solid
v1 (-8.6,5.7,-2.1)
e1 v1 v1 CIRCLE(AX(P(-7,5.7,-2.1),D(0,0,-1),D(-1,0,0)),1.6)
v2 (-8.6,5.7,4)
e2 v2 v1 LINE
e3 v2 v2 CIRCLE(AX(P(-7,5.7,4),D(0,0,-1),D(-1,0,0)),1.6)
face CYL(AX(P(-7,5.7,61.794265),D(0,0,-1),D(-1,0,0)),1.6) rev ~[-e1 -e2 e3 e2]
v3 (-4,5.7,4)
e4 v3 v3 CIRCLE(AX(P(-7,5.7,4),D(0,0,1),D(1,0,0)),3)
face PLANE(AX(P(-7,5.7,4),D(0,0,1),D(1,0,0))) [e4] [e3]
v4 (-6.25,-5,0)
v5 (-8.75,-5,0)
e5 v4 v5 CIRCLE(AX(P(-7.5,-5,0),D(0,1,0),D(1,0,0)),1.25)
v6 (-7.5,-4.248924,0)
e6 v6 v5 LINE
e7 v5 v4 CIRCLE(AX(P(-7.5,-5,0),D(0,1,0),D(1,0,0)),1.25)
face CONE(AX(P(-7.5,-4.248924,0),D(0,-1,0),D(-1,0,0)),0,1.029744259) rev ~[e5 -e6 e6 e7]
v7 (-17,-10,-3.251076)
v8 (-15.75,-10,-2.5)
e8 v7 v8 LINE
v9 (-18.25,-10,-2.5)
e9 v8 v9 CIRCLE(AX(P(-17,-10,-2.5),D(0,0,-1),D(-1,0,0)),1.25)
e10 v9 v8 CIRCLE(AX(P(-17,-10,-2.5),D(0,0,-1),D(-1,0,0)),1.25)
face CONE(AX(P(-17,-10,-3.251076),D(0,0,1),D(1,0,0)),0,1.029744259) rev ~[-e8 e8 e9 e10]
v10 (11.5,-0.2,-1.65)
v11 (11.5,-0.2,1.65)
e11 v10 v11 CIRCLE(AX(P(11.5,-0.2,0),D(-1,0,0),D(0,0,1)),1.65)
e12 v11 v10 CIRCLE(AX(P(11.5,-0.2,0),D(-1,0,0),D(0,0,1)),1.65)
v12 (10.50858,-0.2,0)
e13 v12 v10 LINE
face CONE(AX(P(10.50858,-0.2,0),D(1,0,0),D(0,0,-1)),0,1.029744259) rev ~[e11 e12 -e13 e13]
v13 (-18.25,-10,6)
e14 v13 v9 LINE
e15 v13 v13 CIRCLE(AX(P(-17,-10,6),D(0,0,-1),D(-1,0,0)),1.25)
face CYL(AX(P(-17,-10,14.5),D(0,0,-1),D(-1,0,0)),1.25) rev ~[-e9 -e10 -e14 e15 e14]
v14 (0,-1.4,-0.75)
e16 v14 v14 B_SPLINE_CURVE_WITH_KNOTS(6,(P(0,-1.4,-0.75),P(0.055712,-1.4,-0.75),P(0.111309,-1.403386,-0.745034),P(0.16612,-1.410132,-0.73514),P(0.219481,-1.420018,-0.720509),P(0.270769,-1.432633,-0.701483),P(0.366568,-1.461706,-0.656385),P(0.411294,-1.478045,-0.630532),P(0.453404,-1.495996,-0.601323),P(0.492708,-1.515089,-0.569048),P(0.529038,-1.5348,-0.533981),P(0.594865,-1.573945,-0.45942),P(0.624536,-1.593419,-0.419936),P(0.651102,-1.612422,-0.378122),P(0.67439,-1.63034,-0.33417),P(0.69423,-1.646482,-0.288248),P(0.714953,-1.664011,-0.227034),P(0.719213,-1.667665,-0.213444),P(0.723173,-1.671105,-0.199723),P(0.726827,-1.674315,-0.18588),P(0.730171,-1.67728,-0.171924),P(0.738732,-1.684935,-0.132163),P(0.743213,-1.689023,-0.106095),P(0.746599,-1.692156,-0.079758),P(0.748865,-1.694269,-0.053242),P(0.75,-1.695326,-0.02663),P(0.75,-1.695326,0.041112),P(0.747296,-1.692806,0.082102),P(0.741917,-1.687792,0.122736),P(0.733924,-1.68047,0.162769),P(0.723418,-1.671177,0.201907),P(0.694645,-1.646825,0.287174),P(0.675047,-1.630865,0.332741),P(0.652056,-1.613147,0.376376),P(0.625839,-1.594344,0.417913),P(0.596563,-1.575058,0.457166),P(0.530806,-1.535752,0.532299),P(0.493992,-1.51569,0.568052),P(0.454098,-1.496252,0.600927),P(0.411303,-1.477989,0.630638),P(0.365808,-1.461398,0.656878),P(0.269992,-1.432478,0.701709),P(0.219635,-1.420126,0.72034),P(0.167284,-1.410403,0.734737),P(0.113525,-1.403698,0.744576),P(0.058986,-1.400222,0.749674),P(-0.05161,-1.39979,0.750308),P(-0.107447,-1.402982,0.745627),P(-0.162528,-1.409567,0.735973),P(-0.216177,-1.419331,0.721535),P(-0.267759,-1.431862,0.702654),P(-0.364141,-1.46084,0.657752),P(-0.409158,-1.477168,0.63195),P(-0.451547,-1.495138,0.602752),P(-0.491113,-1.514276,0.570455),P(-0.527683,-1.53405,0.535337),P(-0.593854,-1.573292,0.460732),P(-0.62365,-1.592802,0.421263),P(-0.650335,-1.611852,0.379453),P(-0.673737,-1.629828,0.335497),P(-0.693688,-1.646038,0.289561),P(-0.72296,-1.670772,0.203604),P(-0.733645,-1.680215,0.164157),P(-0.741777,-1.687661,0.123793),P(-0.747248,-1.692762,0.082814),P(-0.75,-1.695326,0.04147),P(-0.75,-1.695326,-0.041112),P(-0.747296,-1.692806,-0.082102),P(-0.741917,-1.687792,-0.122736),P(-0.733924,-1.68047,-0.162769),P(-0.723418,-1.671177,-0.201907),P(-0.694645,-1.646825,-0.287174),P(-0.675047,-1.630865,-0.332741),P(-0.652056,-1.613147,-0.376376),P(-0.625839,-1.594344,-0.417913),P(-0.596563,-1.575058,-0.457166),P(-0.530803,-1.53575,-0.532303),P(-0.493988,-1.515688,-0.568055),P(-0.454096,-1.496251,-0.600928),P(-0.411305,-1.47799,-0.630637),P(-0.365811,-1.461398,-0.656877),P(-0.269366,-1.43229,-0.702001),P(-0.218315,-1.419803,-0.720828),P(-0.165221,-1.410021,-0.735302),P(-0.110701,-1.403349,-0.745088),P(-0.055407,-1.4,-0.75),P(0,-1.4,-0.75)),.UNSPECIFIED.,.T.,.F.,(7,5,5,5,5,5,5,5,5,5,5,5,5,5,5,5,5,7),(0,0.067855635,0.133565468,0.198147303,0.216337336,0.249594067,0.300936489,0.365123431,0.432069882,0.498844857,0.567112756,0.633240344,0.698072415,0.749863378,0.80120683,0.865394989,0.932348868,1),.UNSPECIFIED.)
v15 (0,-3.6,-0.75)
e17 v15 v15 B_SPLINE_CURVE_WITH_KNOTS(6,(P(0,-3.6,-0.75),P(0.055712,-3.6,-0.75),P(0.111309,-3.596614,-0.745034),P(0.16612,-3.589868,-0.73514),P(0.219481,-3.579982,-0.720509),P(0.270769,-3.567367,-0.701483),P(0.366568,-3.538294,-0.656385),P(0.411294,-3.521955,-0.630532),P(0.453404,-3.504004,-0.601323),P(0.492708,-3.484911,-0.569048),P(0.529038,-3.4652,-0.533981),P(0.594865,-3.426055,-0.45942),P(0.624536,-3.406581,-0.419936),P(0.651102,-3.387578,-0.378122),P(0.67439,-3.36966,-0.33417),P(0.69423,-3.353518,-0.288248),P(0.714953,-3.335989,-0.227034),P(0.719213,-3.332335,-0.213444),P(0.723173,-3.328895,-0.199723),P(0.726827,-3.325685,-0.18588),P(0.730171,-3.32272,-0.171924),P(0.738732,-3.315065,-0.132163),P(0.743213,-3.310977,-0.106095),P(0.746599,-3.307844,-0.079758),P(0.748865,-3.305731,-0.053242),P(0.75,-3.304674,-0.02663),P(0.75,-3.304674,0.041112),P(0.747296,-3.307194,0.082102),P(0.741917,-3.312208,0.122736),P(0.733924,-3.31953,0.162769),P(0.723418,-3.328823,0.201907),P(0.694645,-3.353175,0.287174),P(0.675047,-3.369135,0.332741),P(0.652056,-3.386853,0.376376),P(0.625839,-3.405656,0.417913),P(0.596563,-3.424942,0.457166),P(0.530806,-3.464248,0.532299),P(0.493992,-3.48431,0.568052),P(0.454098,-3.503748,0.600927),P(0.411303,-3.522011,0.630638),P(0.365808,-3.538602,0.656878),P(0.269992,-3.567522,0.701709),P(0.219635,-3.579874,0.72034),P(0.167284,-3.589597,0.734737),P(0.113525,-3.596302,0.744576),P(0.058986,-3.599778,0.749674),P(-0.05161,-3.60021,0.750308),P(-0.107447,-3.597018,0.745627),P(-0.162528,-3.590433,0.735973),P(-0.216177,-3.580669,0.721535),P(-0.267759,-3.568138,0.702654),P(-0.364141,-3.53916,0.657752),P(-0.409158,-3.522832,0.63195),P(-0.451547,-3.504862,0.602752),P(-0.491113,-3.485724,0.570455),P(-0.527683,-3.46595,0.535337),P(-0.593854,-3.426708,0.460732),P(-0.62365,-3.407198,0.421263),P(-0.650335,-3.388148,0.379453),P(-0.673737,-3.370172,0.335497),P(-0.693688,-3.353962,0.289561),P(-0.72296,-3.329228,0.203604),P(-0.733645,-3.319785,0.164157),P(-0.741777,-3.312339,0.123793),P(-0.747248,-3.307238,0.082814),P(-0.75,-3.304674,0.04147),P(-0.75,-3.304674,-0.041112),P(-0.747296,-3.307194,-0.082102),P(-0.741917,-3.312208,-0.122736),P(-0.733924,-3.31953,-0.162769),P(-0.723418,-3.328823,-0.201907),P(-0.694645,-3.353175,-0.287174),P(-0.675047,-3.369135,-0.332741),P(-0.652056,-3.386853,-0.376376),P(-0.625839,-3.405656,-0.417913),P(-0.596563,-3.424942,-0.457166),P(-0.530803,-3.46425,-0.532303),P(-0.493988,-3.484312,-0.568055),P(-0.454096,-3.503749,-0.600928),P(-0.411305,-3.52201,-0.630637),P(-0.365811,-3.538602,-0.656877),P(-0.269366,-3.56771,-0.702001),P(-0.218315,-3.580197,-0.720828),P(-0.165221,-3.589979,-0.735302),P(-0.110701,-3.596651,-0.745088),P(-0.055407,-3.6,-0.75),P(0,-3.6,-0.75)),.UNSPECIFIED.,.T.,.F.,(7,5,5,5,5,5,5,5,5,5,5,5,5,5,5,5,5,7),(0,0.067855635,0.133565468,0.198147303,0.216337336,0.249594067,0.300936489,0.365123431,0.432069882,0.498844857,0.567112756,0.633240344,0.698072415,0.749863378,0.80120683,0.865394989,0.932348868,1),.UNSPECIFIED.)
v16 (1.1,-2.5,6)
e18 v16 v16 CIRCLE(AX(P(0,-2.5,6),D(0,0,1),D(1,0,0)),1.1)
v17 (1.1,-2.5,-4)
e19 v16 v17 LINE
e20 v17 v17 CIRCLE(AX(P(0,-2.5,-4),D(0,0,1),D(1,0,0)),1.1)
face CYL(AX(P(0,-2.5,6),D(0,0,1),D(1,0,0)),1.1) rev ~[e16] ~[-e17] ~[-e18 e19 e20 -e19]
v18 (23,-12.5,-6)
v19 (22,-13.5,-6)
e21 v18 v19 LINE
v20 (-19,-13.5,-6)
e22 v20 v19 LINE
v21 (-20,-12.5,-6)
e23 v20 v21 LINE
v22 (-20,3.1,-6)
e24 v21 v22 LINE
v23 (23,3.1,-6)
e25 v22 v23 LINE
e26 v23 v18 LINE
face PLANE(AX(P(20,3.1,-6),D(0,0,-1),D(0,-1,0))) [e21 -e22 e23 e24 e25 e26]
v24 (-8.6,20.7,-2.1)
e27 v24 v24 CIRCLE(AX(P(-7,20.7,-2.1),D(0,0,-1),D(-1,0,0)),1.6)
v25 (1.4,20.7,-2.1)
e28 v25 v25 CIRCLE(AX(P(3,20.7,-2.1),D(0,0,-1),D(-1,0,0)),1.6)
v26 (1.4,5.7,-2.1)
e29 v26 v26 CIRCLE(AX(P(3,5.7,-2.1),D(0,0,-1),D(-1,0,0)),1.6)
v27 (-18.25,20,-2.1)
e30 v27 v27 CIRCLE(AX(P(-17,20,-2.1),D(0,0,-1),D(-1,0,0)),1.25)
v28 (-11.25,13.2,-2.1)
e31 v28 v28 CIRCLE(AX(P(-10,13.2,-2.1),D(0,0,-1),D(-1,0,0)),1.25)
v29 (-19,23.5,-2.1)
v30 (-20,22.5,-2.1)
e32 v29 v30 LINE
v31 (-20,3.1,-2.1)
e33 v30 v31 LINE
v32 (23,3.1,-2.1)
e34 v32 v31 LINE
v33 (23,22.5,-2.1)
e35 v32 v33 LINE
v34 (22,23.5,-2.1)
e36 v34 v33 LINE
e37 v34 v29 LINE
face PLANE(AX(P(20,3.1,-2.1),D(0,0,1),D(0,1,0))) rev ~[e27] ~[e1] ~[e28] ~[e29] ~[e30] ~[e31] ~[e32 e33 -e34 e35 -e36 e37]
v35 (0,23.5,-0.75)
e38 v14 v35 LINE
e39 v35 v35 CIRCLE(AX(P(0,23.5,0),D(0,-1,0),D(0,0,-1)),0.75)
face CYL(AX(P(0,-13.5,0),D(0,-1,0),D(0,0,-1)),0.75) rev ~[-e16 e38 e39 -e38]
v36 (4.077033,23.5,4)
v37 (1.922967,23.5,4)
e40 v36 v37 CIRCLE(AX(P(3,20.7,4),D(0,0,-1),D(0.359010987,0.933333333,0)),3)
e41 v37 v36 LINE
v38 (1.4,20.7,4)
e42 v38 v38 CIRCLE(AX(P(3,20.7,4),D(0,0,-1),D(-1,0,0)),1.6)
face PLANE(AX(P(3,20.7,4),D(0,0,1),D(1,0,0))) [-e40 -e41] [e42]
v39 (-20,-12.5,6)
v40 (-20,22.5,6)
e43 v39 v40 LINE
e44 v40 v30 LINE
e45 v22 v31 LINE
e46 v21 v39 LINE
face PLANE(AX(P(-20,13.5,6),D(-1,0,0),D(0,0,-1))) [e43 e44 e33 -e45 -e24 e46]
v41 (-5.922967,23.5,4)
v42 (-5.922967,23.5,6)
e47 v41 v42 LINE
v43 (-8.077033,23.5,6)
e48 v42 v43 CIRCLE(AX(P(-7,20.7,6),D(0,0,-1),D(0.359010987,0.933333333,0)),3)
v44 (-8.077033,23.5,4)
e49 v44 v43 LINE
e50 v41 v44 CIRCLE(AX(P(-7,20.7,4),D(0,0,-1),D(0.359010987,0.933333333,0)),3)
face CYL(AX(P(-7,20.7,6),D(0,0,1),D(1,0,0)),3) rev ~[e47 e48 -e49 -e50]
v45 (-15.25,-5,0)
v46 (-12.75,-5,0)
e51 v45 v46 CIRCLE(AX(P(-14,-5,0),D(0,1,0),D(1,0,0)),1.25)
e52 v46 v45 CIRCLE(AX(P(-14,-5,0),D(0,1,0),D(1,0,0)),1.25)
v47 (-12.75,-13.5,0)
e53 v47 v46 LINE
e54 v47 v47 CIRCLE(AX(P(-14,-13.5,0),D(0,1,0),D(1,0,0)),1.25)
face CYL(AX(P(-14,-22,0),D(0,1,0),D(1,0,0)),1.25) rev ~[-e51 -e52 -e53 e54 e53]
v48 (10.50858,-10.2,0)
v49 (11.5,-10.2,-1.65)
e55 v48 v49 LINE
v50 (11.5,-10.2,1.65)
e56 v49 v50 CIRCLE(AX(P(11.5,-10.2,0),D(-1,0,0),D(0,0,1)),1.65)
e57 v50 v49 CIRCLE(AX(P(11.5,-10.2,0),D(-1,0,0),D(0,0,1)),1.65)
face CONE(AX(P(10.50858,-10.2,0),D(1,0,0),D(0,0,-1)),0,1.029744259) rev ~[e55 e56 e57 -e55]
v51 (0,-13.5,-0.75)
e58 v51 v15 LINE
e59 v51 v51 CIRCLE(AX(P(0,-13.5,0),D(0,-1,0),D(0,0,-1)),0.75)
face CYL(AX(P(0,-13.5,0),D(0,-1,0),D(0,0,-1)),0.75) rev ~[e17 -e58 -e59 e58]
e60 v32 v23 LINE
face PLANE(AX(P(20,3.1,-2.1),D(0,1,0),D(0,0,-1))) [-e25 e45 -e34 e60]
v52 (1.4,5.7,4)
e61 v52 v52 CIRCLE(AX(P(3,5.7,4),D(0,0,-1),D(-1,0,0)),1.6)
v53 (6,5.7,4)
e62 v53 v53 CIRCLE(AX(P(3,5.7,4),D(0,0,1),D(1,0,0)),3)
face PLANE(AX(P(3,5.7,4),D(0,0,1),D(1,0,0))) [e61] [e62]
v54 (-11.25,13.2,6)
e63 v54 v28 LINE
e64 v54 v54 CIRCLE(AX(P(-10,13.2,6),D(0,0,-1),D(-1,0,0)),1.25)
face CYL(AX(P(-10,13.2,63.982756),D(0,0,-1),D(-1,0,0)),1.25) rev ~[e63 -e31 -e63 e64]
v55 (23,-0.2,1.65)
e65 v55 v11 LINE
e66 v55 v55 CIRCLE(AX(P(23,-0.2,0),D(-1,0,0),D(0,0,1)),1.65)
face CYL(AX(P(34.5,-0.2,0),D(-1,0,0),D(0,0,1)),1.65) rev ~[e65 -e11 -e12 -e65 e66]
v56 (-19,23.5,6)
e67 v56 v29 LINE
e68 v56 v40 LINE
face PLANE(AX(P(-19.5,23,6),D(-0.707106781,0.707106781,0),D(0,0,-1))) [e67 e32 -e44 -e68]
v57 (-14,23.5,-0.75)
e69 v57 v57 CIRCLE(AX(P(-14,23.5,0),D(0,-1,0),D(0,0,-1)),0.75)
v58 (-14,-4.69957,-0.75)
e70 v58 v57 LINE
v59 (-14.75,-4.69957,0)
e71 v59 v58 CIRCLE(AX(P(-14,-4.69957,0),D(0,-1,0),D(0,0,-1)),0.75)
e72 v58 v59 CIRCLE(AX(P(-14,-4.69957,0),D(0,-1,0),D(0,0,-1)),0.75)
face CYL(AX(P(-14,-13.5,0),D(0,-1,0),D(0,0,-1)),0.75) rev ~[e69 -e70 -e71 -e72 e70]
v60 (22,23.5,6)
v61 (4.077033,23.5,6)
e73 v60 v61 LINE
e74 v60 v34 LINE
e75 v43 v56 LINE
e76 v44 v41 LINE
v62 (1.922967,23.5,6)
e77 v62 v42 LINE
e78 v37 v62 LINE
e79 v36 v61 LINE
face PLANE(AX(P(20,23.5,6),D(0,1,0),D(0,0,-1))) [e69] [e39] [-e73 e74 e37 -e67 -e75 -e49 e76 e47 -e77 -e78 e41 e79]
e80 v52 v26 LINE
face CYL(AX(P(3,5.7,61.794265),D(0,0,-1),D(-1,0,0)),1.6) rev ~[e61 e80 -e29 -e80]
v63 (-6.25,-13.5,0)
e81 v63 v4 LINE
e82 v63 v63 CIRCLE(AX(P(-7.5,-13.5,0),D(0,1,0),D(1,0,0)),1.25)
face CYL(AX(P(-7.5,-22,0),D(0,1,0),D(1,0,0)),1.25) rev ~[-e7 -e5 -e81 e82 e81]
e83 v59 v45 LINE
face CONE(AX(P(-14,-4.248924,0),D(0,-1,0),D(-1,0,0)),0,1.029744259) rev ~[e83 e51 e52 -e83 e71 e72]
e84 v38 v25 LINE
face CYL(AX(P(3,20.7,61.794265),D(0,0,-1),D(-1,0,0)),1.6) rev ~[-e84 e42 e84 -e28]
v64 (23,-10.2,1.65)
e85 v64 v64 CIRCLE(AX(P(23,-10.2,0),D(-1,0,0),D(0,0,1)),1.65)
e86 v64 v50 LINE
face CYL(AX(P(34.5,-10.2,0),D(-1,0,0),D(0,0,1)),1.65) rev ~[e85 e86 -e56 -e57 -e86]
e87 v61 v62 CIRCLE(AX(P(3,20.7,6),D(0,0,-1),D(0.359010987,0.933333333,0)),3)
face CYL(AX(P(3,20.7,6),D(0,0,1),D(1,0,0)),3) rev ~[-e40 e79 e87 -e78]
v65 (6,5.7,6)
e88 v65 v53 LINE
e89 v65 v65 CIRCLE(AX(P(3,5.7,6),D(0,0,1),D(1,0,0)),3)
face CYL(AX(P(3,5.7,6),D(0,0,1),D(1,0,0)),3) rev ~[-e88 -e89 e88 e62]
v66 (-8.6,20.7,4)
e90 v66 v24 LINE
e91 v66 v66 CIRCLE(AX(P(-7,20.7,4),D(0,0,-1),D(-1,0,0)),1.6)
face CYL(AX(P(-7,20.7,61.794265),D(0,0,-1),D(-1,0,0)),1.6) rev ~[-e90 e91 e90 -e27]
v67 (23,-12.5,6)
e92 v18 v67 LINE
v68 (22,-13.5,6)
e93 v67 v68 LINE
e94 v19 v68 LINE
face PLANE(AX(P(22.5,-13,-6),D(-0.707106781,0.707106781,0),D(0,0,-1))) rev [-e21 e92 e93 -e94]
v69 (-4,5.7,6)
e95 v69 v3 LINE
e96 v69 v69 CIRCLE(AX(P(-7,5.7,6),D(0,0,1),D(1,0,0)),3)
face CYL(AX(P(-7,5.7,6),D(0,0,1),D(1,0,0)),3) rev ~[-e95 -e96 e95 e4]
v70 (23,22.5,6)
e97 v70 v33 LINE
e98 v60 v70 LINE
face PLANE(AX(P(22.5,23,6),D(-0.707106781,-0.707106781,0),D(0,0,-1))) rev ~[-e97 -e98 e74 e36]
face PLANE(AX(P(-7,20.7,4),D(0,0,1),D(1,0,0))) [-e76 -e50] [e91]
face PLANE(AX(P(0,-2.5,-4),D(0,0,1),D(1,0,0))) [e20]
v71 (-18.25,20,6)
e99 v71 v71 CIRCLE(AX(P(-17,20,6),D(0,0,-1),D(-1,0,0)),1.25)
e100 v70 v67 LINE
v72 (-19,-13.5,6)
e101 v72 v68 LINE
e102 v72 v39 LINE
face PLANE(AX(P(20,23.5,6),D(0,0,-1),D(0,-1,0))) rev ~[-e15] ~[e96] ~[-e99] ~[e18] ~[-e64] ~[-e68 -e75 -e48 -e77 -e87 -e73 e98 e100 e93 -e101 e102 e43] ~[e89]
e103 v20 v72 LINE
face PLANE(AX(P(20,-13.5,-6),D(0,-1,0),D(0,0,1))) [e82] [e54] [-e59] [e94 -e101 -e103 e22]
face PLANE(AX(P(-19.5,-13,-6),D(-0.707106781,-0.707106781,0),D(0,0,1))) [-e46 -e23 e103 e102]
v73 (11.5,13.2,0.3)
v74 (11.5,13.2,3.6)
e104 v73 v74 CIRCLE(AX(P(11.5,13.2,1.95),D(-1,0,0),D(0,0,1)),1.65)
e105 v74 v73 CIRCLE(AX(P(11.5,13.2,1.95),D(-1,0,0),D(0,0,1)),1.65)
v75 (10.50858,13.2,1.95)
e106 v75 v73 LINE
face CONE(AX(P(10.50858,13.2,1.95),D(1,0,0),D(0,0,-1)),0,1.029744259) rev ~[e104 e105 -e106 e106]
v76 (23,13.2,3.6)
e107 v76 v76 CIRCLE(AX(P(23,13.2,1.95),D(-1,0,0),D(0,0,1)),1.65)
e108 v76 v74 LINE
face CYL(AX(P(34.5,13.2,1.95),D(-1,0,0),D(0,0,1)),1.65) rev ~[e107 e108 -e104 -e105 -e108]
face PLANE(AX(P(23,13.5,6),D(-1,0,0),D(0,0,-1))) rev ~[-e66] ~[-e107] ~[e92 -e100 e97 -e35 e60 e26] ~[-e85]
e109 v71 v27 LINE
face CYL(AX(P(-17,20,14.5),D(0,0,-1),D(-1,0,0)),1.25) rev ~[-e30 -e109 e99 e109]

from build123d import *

# Parameters (mm, degrees)
SKETCH_1_W              = 40
SKETCH_1_H              = 27
EXTRUDE_1_DEPTH         = 6
SKETCH_2_R              = 1.1
CUT_EXTRUDE_1_DEPTH     = 10
MOVE_FACE_1_BY          = 10
SKETCH_3_W              = 3.9
SKETCH_3_H              = 20.4
CUT_EXTRUDE_2_DEPTH     = 63
HOLE_WIZARD_3_2_3_2_1_D = 3.2
MOVE_FACE_3_BY          = 3
HOLE_WIZARD_M4_2_D      = 3.3
HOLE_WIZARD_M4_2_DEPTH  = 11.5
HOLE_WIZARD_M4_2_TIP    = 0.991420021
SKETCH_16_R             = 3
CUT_EXTRUDE_3_DEPTH     = 2
HOLE_WIZARD_M3_1_D      = 2.5
HOLE_WIZARD_M3_1_DEPTH  = 8.5
HOLE_WIZARD_M3_1_TIP    = 0.751075774
CHAMFER_1_SIZE          = 1
SKETCH_20_R             = 0.75
CUT_EXTRUDE_4_DEPTH     = 66
PATTERN_LINEAR_1_COUNT  = 2
PATTERN_LINEAR_1_PITCH  = 14
HOLE_WIZARD_M3_2_D      = 2.5
HOLE_WIZARD_M3_3_D      = 2.5
HOLE_WIZARD_M3_3_DEPTH  = 8.5
HOLE_WIZARD_M3_3_TIP    = 0.751075774
HOLE_WIZARD_M4_3_D      = 3.3
HOLE_WIZARD_M4_3_DEPTH  = 11.5
HOLE_WIZARD_M4_3_TIP    = 0.991420021


with BuildPart() as part:
    # 草图1 → 凸台-拉伸1 (new, symmetric)
    with BuildSketch(Plane.XY):
        Rectangle(SKETCH_1_W, SKETCH_1_H)
    extrude(amount=EXTRUDE_1_DEPTH, both=True)

    # 草图2 → 切除-拉伸1 (cut)
    with BuildSketch(Plane.XY.offset(6)):
        with Locations((0, -2.5)):
            Circle(SKETCH_2_R)
    extrude(amount=-CUT_EXTRUDE_1_DEPTH, mode=Mode.SUBTRACT)

    # Move Face 1: a face moved outward by 10.0
    extrude(part.faces().sort_by_distance((0, 13.5, 0))[0], amount=MOVE_FACE_1_BY, dir=(0, 1, 0))

    # 草图3 → 切除-拉伸2 (cut)
    with BuildSketch(Plane(origin=(20, 0, 0), x_dir=(0, 0, -1), z_dir=(1, 0, 0))):
        with Locations((4.05, 13.3)):
            Rectangle(SKETCH_3_W, SKETCH_3_H)
    extrude(amount=-CUT_EXTRUDE_2_DEPTH, mode=Mode.SUBTRACT)

    # Ø3.2 (3.2) 直径孔1 (through all)
    with Locations(Plane.XY.offset(6)):
        with Locations((3, 20.7), (-7, 20.7), (-7, 5.7), (3, 5.7)):
            Hole(HOLE_WIZARD_3_2_3_2_1_D / 2)

    # Move Face 3: a face moved outward by 3.0
    extrude(part.faces().sort_by_distance((20, 3.188047415, 0.884145538))[0], amount=MOVE_FACE_3_BY, dir=(1, 0, 0))

    # M4 螺纹孔2
    with Locations(Plane(origin=(23, 0, 0), x_dir=(0, 0, -1), z_dir=(1, 0, 0))):
        with Locations((0, -0.2), (0, -10.2)):
            Hole(HOLE_WIZARD_M4_2_D / 2, depth=HOLE_WIZARD_M4_2_DEPTH)
            with Locations((0, 0, -(HOLE_WIZARD_M4_2_DEPTH + HOLE_WIZARD_M4_2_TIP / 2))):  # 118° drill point
                Cone(0, HOLE_WIZARD_M4_2_D / 2, HOLE_WIZARD_M4_2_TIP, mode=Mode.SUBTRACT)

    # 草图16 → 切除-拉伸3 (cut)
    with BuildSketch(Plane.XY.offset(6)):
        with Locations((-7, 20.7)):
            Circle(SKETCH_16_R)
        with Locations((3, 20.7)):
            Circle(SKETCH_16_R)
        with Locations((-7, 5.7)):
            Circle(SKETCH_16_R)
        with Locations((3, 5.7)):
            Circle(SKETCH_16_R)
    extrude(amount=-CUT_EXTRUDE_3_DEPTH, mode=Mode.SUBTRACT)

    # M3 螺纹孔1
    with Locations(Plane.XY.offset(6)):
        with Locations((-17, 20), (-17, -10)):
            Hole(HOLE_WIZARD_M3_1_D / 2, depth=HOLE_WIZARD_M3_1_DEPTH)
            with Locations((0, 0, -(HOLE_WIZARD_M3_1_DEPTH + HOLE_WIZARD_M3_1_TIP / 2))):  # 118° drill point
                Cone(0, HOLE_WIZARD_M3_1_D / 2, HOLE_WIZARD_M3_1_TIP, mode=Mode.SUBTRACT)

    # 倒角1
    chamfer_1_edges = [part.edges().sort_by_distance(p)[0] for p in [
        (23, -13.5, 0),
        (-20, -13.5, 0),
        (-20, 23.5, 1.95),
        (23, 23.5, 1.95),
    ]]
    chamfer(chamfer_1_edges, length=CHAMFER_1_SIZE)

    # 草图20 → 切除-拉伸4 (cut)
    with BuildSketch(Plane.XZ.offset(13.5)):
        with Locations(Location((0, 0, 0), (0, 0, 270))):
            Circle(SKETCH_20_R)
    cut_extrude_4 = extrude(amount=-CUT_EXTRUDE_4_DEPTH, mode=Mode.SUBTRACT)

    # 阵列(线性)1: 切除-拉伸4 ×2
    with Locations(*[(-i * PATTERN_LINEAR_1_PITCH, 0, 0) for i in range(1, PATTERN_LINEAR_1_COUNT)]):
        add(cut_extrude_4, mode=Mode.SUBTRACT)

    # M3 螺纹孔2 (through all)
    with Locations(Plane.XY.offset(6)):
        with Locations((-10, 13.2)):
            Hole(HOLE_WIZARD_M3_2_D / 2)

    # M3 螺纹孔3
    with Locations(Plane(origin=(0, -13.5, 0), x_dir=(-1, 0, 0), z_dir=(0, -1, 0))):
        with Locations((7.5, 0), (14, 0)):
            Hole(HOLE_WIZARD_M3_3_D / 2, depth=HOLE_WIZARD_M3_3_DEPTH)
            with Locations((0, 0, -(HOLE_WIZARD_M3_3_DEPTH + HOLE_WIZARD_M3_3_TIP / 2))):  # 118° drill point
                Cone(0, HOLE_WIZARD_M3_3_D / 2, HOLE_WIZARD_M3_3_TIP, mode=Mode.SUBTRACT)

    # M4 螺纹孔3
    with Locations(Plane(origin=(23, 0, 0), x_dir=(0, 0, -1), z_dir=(1, 0, 0))):
        with Locations((-1.95, 13.2)):
            Hole(HOLE_WIZARD_M4_3_D / 2, depth=HOLE_WIZARD_M4_3_DEPTH)
            with Locations((0, 0, -(HOLE_WIZARD_M4_3_DEPTH + HOLE_WIZARD_M4_3_TIP / 2))):  # 118° drill point
                Cone(0, HOLE_WIZARD_M4_3_D / 2, HOLE_WIZARD_M4_3_TIP, mode=Mode.SUBTRACT)


solid = part.part
